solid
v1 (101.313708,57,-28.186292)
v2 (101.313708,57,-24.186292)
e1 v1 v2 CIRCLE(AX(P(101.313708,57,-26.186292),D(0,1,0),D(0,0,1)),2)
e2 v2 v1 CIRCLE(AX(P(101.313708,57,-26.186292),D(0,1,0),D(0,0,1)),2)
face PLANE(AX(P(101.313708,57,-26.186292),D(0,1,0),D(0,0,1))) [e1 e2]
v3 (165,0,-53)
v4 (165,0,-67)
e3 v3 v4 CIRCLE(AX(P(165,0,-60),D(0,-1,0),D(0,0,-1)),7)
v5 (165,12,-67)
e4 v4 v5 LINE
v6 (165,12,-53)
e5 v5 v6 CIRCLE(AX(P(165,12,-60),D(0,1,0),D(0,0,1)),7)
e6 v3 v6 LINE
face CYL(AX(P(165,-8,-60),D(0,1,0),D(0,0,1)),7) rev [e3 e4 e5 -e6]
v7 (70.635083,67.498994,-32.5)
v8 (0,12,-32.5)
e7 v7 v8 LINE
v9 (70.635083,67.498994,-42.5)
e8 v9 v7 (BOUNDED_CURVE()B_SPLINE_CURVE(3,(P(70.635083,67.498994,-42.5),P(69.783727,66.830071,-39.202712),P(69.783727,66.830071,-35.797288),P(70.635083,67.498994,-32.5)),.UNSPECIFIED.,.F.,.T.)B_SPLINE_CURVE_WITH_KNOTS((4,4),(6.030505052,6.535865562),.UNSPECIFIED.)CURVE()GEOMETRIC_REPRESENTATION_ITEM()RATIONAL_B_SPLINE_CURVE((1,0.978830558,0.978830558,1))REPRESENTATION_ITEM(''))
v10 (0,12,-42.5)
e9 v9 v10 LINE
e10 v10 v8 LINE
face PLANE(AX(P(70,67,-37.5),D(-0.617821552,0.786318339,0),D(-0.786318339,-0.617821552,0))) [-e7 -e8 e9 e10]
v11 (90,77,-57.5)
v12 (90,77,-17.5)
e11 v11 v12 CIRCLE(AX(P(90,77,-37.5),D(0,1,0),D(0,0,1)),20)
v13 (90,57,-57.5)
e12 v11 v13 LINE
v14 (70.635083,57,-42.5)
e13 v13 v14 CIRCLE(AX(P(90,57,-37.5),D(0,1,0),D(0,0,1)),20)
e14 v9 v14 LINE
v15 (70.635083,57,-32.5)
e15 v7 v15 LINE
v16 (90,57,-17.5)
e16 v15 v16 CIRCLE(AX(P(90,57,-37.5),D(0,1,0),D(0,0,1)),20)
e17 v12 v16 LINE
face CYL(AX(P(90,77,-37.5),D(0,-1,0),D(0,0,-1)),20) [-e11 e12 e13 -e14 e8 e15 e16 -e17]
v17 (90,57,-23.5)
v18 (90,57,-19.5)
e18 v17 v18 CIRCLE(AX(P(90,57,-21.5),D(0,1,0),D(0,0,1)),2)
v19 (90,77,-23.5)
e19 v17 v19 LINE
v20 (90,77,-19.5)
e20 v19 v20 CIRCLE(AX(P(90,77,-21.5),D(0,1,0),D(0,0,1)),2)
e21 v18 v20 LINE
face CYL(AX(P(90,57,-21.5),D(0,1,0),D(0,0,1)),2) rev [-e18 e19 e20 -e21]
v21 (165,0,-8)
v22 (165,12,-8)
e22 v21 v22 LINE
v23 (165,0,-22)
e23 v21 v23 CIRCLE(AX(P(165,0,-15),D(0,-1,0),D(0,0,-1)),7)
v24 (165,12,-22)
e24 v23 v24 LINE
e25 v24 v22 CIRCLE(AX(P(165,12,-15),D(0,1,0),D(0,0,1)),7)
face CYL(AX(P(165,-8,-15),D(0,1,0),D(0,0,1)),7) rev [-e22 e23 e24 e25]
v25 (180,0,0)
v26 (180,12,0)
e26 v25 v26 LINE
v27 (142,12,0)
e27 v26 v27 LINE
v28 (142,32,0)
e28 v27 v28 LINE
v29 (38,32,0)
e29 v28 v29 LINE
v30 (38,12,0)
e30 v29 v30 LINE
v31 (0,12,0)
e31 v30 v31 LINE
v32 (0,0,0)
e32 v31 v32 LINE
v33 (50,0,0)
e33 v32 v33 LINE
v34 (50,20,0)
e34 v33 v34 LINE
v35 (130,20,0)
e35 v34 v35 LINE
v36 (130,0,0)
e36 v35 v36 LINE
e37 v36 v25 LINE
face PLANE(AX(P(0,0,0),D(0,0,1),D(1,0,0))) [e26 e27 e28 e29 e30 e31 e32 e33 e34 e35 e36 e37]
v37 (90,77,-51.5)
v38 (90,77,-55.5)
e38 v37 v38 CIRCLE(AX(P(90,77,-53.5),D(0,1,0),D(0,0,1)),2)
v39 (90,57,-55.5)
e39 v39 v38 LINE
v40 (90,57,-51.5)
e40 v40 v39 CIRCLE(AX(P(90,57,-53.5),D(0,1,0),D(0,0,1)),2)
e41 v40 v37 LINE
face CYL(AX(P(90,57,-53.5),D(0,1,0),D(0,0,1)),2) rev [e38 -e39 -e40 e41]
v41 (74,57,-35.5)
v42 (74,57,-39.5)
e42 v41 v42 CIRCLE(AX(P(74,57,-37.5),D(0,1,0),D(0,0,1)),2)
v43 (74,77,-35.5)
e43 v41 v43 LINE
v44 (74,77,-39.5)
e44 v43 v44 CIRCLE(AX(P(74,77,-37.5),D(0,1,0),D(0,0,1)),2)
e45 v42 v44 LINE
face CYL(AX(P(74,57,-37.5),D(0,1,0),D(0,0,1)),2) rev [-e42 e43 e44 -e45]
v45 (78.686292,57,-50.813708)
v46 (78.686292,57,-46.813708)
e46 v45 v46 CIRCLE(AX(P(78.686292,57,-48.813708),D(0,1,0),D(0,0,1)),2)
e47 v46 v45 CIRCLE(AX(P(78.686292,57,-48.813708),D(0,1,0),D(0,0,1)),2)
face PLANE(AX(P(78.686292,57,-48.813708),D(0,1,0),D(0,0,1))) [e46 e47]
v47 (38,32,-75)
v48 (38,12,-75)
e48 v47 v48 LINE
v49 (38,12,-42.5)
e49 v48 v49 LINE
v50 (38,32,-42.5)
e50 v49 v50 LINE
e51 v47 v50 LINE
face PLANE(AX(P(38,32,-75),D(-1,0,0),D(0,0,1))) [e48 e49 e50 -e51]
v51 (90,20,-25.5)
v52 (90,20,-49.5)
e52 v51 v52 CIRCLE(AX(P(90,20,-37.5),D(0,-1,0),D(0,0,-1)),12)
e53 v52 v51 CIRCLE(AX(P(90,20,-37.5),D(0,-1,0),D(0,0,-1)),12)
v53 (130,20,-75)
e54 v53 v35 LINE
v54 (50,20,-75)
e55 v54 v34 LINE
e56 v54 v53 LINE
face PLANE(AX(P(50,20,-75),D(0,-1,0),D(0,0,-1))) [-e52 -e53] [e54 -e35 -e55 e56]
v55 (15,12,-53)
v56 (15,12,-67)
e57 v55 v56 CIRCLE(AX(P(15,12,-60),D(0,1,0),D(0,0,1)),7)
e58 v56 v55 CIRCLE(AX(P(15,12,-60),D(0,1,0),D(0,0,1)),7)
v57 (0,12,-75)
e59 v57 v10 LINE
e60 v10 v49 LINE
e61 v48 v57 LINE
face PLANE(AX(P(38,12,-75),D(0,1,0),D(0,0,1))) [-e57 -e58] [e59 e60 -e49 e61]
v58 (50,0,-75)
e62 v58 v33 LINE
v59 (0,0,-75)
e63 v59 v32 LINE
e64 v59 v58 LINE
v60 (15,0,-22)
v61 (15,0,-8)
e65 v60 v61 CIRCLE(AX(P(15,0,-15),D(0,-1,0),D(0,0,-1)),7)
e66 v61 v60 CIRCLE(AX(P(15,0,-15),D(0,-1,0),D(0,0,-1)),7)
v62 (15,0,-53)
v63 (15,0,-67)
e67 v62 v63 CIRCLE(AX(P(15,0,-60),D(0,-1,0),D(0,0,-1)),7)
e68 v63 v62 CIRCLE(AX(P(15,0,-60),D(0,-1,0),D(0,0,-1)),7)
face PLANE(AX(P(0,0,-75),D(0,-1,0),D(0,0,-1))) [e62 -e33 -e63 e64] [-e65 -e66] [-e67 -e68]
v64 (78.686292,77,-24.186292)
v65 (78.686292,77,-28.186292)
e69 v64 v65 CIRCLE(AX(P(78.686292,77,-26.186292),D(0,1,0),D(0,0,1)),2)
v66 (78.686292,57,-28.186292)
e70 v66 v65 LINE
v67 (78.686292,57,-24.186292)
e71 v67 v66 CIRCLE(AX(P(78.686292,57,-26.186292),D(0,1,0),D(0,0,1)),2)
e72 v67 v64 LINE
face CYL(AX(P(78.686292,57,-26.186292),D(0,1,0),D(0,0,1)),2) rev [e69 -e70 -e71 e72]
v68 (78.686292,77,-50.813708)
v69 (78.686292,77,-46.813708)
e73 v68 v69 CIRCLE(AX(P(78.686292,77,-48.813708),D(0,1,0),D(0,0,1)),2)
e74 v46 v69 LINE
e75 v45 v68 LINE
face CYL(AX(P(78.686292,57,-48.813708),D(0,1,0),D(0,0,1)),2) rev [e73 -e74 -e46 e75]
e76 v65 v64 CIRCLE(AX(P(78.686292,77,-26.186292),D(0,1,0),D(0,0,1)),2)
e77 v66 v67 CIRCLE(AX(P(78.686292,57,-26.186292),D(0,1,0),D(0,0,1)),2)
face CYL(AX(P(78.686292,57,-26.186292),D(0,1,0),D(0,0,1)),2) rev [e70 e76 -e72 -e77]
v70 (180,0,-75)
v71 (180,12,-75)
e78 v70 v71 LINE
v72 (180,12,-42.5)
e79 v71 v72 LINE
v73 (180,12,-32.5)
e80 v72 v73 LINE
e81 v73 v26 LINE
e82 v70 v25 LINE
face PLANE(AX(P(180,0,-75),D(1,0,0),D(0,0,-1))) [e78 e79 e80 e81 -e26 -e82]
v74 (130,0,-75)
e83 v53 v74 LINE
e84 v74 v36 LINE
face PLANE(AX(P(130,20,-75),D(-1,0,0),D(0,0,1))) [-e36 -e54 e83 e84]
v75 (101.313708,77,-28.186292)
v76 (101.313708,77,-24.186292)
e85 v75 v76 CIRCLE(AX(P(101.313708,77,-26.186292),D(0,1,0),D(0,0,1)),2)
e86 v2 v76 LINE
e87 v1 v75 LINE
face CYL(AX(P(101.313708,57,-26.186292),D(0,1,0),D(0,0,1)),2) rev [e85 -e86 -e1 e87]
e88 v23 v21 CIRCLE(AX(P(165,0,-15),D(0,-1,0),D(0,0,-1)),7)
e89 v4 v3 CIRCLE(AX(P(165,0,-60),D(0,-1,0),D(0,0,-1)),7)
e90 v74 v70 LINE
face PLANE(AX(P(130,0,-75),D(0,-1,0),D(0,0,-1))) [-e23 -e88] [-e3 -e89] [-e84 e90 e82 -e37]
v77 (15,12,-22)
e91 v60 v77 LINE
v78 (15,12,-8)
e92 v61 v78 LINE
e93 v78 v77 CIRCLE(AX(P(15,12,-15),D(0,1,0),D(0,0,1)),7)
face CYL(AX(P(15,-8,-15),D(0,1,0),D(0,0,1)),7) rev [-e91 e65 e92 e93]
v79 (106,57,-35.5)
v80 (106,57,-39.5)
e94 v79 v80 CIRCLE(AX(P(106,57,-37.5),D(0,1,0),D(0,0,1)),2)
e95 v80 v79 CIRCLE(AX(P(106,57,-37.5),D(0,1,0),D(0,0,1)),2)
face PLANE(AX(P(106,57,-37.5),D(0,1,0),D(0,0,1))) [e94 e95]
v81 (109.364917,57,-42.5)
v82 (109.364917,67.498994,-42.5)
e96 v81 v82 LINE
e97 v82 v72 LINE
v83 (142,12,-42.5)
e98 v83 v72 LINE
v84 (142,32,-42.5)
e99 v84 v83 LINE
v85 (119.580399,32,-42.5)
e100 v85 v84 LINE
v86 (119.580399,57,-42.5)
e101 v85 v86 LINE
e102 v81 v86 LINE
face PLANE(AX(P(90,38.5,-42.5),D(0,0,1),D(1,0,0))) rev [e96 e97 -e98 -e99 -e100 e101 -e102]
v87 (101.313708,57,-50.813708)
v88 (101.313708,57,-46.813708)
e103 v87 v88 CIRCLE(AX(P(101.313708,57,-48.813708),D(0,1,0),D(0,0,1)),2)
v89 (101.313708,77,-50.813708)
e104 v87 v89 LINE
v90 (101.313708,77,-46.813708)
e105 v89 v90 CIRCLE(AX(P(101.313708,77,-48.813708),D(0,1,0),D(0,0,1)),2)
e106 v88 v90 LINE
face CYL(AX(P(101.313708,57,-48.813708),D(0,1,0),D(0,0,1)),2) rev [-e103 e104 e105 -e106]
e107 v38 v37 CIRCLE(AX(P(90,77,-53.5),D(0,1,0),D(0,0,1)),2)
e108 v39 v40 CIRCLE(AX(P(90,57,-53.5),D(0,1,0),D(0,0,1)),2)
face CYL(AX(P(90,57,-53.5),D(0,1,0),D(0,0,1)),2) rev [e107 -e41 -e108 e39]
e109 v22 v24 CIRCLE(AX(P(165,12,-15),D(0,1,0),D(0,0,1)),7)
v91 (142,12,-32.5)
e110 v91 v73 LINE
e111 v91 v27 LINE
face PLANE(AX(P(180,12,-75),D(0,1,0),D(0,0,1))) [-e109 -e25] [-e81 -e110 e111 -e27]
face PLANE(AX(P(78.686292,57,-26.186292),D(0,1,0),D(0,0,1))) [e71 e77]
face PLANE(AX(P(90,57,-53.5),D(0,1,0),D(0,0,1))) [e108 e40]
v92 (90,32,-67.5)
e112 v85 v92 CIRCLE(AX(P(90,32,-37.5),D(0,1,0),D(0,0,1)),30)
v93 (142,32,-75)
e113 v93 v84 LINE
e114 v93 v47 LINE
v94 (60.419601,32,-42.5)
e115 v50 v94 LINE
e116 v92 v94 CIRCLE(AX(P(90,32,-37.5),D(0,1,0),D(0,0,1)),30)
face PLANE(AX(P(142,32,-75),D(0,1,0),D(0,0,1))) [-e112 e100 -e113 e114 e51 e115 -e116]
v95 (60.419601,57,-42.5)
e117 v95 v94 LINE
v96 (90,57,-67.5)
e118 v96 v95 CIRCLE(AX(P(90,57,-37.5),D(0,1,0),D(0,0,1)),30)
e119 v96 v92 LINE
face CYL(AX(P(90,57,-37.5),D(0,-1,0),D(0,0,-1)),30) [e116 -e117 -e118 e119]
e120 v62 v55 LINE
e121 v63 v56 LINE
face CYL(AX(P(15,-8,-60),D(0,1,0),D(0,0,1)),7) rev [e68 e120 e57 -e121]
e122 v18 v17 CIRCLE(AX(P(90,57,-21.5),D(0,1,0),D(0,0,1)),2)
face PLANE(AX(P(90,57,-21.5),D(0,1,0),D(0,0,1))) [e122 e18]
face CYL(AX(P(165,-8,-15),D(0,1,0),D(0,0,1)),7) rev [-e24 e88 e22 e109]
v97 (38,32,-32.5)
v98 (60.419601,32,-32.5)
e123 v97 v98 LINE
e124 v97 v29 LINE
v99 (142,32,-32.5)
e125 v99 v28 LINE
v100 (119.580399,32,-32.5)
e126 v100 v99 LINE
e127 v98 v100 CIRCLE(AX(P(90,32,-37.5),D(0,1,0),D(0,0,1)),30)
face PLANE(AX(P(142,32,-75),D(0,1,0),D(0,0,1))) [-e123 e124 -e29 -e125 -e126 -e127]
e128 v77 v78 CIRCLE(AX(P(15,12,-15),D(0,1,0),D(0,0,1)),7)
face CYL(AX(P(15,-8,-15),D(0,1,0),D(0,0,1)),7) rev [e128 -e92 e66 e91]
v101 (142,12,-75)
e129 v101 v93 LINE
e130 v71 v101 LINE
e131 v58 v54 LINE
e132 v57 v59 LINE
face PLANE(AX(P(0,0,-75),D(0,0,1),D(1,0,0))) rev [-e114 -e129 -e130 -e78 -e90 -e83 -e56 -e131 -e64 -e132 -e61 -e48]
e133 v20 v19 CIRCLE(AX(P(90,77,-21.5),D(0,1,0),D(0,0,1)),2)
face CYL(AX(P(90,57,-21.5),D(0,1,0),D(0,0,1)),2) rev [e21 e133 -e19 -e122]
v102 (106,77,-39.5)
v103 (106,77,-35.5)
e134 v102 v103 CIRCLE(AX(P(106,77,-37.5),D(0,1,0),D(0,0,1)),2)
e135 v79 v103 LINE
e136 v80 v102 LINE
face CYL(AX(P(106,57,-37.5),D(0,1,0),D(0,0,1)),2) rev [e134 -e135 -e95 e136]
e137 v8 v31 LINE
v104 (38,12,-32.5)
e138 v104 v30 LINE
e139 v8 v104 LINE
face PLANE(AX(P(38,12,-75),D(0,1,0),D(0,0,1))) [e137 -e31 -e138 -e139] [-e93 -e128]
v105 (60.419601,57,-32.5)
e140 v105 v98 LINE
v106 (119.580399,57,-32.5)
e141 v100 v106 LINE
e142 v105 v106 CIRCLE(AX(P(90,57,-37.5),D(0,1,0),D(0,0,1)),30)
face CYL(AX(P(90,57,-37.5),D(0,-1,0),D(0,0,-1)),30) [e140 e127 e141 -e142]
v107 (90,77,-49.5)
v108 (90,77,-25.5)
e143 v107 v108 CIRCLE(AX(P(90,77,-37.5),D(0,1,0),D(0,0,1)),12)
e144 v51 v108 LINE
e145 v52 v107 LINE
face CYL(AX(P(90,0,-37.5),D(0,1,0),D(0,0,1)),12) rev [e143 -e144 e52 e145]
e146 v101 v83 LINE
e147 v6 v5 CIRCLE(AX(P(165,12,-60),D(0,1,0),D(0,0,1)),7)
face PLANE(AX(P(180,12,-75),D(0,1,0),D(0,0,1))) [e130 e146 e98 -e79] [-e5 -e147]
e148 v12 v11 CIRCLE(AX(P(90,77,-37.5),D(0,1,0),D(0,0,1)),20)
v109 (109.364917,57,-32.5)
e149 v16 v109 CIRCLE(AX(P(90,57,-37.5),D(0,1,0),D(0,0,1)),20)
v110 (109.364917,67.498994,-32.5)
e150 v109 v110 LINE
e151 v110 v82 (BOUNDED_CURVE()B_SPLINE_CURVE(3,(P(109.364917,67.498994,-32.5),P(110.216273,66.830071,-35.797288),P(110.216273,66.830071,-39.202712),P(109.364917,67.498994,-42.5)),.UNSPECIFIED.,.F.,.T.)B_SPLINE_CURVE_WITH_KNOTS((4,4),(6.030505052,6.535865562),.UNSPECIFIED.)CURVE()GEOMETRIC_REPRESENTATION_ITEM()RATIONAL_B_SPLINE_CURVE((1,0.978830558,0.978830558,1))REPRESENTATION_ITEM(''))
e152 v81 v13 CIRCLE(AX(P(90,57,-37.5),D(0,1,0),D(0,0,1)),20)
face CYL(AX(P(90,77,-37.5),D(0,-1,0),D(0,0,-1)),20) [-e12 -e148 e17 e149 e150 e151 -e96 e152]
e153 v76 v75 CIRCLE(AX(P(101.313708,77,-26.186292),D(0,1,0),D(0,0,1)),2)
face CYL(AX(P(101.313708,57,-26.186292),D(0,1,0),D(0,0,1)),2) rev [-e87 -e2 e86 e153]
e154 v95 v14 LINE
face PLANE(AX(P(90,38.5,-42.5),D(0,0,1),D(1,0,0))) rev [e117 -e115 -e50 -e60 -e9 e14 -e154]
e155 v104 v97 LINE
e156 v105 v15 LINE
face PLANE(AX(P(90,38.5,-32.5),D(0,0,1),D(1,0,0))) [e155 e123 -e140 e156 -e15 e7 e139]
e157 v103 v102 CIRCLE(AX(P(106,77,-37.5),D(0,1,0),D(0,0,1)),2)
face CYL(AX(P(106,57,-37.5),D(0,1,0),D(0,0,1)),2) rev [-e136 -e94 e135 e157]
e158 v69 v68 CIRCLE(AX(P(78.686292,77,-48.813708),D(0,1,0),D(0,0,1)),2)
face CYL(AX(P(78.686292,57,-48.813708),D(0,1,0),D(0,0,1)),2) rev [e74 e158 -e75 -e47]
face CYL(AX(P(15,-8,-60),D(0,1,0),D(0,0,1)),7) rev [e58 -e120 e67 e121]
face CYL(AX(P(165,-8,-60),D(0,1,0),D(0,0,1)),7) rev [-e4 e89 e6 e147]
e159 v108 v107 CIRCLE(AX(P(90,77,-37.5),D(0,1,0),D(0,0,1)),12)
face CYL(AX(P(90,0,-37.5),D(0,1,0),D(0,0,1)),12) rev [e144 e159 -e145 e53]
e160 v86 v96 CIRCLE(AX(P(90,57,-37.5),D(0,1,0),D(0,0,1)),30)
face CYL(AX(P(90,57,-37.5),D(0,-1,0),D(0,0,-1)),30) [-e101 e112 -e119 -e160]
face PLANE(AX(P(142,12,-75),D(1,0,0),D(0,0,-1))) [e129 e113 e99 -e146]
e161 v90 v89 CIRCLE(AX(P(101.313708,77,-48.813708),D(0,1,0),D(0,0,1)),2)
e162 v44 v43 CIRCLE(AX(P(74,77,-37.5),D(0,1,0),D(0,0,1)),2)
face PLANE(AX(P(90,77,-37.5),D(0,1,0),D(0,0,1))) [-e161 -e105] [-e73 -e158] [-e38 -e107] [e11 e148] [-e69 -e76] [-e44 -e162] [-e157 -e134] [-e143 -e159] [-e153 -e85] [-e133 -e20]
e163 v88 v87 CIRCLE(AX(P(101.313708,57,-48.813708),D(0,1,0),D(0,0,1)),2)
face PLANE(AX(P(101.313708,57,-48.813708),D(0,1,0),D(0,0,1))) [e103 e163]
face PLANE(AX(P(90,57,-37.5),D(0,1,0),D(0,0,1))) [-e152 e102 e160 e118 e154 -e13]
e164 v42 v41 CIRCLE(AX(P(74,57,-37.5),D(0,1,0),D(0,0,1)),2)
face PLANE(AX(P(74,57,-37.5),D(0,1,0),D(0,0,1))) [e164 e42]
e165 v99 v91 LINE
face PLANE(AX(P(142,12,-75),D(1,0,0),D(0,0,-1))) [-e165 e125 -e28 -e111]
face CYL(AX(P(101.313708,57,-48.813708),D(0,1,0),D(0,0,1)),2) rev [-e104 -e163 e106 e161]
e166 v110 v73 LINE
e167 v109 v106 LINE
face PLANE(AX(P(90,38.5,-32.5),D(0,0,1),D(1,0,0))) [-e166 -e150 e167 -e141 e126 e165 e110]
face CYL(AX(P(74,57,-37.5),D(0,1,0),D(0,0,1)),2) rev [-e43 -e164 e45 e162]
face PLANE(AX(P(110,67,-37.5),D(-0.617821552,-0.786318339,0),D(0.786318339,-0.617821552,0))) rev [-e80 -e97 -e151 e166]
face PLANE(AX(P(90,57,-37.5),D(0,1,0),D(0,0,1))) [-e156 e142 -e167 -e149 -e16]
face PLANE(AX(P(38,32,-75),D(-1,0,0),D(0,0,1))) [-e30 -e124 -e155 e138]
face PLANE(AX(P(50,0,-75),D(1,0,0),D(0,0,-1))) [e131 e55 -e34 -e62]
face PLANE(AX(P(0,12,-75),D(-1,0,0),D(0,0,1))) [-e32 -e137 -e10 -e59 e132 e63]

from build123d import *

# Parameters (mm, degrees)
BASE_PLATE_DEPTH              = 75
BOSS_60_SKETCH_R              = 30
BOSS_60_DEPTH                 = 25
HUB_40_SKETCH_R               = 20
HUB_40_DEPTH                  = 20
BOLT_CIRCLE_8X_4_SKETCH_R     = 2
BOLT_CIRCLE_HOLES_8X_4_DEPTH  = 20
BORE_24_SKETCH_R              = 12
BORE_24_DEPTH                 = 210.652092763
MOUNTING_HOLES_4X_14_SKETCH_R = 7
MOUNTING_HOLES_4X_14_DEPTH    = 20
REINFORCING_RIB_A_REACH       = 201.337
RIB_A_SKETCH_WALL_W           = 489.696521402
RIB_A_SKETCH_WALL_H           = 10
REINFORCING_RIB_B_REACH       = 201.337
RIB_B_SKETCH_WALL_W           = 489.696521402
RIB_B_SKETCH_WALL_H           = 10


with BuildPart() as part:
    # Base Plate Profile → Base Plate (new body)
    with BuildSketch(Plane.XY):
        Polygon((0, 0), (50, 0), (50, 20), (130, 20), (130, 0), (180, 0), (180, 12), (142, 12), (142, 32), (38, 32), (38, 12), (0, 12), align=None)
    extrude(amount=-BASE_PLATE_DEPTH)

    # Boss Ø60 Sketch → Boss Ø60 (add)
    with BuildSketch(Plane(origin=(0, 32, 0), x_dir=(1, 0, 0), z_dir=(0, 1, 0))):
        with Locations(Location((90, 37.5, 0), (0, 0, 270))):
            Circle(BOSS_60_SKETCH_R)
    extrude(amount=BOSS_60_DEPTH)

    # Hub Ø40 Sketch → Hub Ø40 (add)
    with BuildSketch(Plane(origin=(0, 57, 0), x_dir=(1, 0, 0), z_dir=(0, 1, 0))):
        with Locations(Location((90, 37.5, 0), (0, 0, 270))):
            Circle(HUB_40_SKETCH_R)
    extrude(amount=HUB_40_DEPTH)

    # Bolt Circle 8xØ4 Sketch → Bolt Circle Holes 8xØ4 (cut)
    with BuildSketch(Plane(origin=(0, 77, 0), x_dir=(1, 0, 0), z_dir=(0, 1, 0))):
        with Locations(Location((90, 53.5, 0), (0, 0, 270))):
            Circle(BOLT_CIRCLE_8X_4_SKETCH_R)
        with Locations(Location((101.313708499, 48.813708499, 0), (0, 0, 270))):
            Circle(BOLT_CIRCLE_8X_4_SKETCH_R)
        with Locations(Location((106, 37.5, 0), (0, 0, 270))):
            Circle(BOLT_CIRCLE_8X_4_SKETCH_R)
        with Locations(Location((101.313708499, 26.186291501, 0), (0, 0, 270))):
            Circle(BOLT_CIRCLE_8X_4_SKETCH_R)
        with Locations(Location((90, 21.5, 0), (0, 0, 270))):
            Circle(BOLT_CIRCLE_8X_4_SKETCH_R)
        with Locations(Location((78.686291501, 26.186291501, 0), (0, 0, 270))):
            Circle(BOLT_CIRCLE_8X_4_SKETCH_R)
        with Locations(Location((74, 37.5, 0), (0, 0, 270))):
            Circle(BOLT_CIRCLE_8X_4_SKETCH_R)
        with Locations(Location((78.686291501, 48.813708499, 0), (0, 0, 270))):
            Circle(BOLT_CIRCLE_8X_4_SKETCH_R)
    extrude(amount=-BOLT_CIRCLE_HOLES_8X_4_DEPTH, mode=Mode.SUBTRACT)

    # Bore Ø24 Sketch → Bore Ø24 (cut, through all)
    with BuildSketch(Plane(origin=(0, 77, 0), x_dir=(1, 0, 0), z_dir=(0, 1, 0))):
        with Locations(Location((90, 37.5, 0), (0, 0, 270))):
            Circle(BORE_24_SKETCH_R)
    extrude(amount=-BORE_24_DEPTH, mode=Mode.SUBTRACT)

    # Mounting Holes 4xØ14 Sketch → Mounting Holes 4xØ14 (cut)
    with BuildSketch(Plane(origin=(0, 12, 0), x_dir=(1, 0, 0), z_dir=(0, 1, 0))):
        with Locations(Location((165, 60, 0), (0, 0, 270))):
            Circle(MOUNTING_HOLES_4X_14_SKETCH_R)
        with Locations(Location((165, 15, 0), (0, 0, 270))):
            Circle(MOUNTING_HOLES_4X_14_SKETCH_R)
        with Locations(Location((15, 60, 0), (0, 0, 270))):
            Circle(MOUNTING_HOLES_4X_14_SKETCH_R)
        with Locations(Location((15, 15, 0), (0, 0, 270))):
            Circle(MOUNTING_HOLES_4X_14_SKETCH_R)
    extrude(amount=-MOUNTING_HOLES_4X_14_DEPTH, mode=Mode.SUBTRACT)

    # Rib A Sketch wall → Reinforcing Rib A (add, up to next)
    with BuildSketch(Plane(origin=(145, 39.5, -37.5), x_dir=(0.786318338822, -0.617821551932, 0), z_dir=(0.617821551932, 0.786318338822, 0)), mode=Mode.PRIVATE) as reinforcing_rib_a_sk1:
        Rectangle(RIB_A_SKETCH_WALL_W, RIB_A_SKETCH_WALL_H)
    reinforcing_rib_a_tool1 = extrude(reinforcing_rib_a_sk1.sketch, amount=-REINFORCING_RIB_A_REACH, mode=Mode.PRIVATE) - part.part
    add(reinforcing_rib_a_tool1.solids().sort_by_distance((145, 39.5, -37.5))[0])

    # Rib B Sketch wall → Reinforcing Rib B (add, up to next)
    with BuildSketch(Plane(origin=(35, 39.5, -37.5), x_dir=(-0.786318338822, -0.617821551932, 0), z_dir=(0.617821551932, -0.786318338822, 0)), mode=Mode.PRIVATE) as reinforcing_rib_b_sk1:
        Rectangle(RIB_B_SKETCH_WALL_W, RIB_B_SKETCH_WALL_H)
    reinforcing_rib_b_tool1 = extrude(reinforcing_rib_b_sk1.sketch, amount=REINFORCING_RIB_B_REACH, mode=Mode.PRIVATE) - part.part
    add(reinforcing_rib_b_tool1.solids().sort_by_distance((35, 39.5, -37.5))[0])


solid = part.part
